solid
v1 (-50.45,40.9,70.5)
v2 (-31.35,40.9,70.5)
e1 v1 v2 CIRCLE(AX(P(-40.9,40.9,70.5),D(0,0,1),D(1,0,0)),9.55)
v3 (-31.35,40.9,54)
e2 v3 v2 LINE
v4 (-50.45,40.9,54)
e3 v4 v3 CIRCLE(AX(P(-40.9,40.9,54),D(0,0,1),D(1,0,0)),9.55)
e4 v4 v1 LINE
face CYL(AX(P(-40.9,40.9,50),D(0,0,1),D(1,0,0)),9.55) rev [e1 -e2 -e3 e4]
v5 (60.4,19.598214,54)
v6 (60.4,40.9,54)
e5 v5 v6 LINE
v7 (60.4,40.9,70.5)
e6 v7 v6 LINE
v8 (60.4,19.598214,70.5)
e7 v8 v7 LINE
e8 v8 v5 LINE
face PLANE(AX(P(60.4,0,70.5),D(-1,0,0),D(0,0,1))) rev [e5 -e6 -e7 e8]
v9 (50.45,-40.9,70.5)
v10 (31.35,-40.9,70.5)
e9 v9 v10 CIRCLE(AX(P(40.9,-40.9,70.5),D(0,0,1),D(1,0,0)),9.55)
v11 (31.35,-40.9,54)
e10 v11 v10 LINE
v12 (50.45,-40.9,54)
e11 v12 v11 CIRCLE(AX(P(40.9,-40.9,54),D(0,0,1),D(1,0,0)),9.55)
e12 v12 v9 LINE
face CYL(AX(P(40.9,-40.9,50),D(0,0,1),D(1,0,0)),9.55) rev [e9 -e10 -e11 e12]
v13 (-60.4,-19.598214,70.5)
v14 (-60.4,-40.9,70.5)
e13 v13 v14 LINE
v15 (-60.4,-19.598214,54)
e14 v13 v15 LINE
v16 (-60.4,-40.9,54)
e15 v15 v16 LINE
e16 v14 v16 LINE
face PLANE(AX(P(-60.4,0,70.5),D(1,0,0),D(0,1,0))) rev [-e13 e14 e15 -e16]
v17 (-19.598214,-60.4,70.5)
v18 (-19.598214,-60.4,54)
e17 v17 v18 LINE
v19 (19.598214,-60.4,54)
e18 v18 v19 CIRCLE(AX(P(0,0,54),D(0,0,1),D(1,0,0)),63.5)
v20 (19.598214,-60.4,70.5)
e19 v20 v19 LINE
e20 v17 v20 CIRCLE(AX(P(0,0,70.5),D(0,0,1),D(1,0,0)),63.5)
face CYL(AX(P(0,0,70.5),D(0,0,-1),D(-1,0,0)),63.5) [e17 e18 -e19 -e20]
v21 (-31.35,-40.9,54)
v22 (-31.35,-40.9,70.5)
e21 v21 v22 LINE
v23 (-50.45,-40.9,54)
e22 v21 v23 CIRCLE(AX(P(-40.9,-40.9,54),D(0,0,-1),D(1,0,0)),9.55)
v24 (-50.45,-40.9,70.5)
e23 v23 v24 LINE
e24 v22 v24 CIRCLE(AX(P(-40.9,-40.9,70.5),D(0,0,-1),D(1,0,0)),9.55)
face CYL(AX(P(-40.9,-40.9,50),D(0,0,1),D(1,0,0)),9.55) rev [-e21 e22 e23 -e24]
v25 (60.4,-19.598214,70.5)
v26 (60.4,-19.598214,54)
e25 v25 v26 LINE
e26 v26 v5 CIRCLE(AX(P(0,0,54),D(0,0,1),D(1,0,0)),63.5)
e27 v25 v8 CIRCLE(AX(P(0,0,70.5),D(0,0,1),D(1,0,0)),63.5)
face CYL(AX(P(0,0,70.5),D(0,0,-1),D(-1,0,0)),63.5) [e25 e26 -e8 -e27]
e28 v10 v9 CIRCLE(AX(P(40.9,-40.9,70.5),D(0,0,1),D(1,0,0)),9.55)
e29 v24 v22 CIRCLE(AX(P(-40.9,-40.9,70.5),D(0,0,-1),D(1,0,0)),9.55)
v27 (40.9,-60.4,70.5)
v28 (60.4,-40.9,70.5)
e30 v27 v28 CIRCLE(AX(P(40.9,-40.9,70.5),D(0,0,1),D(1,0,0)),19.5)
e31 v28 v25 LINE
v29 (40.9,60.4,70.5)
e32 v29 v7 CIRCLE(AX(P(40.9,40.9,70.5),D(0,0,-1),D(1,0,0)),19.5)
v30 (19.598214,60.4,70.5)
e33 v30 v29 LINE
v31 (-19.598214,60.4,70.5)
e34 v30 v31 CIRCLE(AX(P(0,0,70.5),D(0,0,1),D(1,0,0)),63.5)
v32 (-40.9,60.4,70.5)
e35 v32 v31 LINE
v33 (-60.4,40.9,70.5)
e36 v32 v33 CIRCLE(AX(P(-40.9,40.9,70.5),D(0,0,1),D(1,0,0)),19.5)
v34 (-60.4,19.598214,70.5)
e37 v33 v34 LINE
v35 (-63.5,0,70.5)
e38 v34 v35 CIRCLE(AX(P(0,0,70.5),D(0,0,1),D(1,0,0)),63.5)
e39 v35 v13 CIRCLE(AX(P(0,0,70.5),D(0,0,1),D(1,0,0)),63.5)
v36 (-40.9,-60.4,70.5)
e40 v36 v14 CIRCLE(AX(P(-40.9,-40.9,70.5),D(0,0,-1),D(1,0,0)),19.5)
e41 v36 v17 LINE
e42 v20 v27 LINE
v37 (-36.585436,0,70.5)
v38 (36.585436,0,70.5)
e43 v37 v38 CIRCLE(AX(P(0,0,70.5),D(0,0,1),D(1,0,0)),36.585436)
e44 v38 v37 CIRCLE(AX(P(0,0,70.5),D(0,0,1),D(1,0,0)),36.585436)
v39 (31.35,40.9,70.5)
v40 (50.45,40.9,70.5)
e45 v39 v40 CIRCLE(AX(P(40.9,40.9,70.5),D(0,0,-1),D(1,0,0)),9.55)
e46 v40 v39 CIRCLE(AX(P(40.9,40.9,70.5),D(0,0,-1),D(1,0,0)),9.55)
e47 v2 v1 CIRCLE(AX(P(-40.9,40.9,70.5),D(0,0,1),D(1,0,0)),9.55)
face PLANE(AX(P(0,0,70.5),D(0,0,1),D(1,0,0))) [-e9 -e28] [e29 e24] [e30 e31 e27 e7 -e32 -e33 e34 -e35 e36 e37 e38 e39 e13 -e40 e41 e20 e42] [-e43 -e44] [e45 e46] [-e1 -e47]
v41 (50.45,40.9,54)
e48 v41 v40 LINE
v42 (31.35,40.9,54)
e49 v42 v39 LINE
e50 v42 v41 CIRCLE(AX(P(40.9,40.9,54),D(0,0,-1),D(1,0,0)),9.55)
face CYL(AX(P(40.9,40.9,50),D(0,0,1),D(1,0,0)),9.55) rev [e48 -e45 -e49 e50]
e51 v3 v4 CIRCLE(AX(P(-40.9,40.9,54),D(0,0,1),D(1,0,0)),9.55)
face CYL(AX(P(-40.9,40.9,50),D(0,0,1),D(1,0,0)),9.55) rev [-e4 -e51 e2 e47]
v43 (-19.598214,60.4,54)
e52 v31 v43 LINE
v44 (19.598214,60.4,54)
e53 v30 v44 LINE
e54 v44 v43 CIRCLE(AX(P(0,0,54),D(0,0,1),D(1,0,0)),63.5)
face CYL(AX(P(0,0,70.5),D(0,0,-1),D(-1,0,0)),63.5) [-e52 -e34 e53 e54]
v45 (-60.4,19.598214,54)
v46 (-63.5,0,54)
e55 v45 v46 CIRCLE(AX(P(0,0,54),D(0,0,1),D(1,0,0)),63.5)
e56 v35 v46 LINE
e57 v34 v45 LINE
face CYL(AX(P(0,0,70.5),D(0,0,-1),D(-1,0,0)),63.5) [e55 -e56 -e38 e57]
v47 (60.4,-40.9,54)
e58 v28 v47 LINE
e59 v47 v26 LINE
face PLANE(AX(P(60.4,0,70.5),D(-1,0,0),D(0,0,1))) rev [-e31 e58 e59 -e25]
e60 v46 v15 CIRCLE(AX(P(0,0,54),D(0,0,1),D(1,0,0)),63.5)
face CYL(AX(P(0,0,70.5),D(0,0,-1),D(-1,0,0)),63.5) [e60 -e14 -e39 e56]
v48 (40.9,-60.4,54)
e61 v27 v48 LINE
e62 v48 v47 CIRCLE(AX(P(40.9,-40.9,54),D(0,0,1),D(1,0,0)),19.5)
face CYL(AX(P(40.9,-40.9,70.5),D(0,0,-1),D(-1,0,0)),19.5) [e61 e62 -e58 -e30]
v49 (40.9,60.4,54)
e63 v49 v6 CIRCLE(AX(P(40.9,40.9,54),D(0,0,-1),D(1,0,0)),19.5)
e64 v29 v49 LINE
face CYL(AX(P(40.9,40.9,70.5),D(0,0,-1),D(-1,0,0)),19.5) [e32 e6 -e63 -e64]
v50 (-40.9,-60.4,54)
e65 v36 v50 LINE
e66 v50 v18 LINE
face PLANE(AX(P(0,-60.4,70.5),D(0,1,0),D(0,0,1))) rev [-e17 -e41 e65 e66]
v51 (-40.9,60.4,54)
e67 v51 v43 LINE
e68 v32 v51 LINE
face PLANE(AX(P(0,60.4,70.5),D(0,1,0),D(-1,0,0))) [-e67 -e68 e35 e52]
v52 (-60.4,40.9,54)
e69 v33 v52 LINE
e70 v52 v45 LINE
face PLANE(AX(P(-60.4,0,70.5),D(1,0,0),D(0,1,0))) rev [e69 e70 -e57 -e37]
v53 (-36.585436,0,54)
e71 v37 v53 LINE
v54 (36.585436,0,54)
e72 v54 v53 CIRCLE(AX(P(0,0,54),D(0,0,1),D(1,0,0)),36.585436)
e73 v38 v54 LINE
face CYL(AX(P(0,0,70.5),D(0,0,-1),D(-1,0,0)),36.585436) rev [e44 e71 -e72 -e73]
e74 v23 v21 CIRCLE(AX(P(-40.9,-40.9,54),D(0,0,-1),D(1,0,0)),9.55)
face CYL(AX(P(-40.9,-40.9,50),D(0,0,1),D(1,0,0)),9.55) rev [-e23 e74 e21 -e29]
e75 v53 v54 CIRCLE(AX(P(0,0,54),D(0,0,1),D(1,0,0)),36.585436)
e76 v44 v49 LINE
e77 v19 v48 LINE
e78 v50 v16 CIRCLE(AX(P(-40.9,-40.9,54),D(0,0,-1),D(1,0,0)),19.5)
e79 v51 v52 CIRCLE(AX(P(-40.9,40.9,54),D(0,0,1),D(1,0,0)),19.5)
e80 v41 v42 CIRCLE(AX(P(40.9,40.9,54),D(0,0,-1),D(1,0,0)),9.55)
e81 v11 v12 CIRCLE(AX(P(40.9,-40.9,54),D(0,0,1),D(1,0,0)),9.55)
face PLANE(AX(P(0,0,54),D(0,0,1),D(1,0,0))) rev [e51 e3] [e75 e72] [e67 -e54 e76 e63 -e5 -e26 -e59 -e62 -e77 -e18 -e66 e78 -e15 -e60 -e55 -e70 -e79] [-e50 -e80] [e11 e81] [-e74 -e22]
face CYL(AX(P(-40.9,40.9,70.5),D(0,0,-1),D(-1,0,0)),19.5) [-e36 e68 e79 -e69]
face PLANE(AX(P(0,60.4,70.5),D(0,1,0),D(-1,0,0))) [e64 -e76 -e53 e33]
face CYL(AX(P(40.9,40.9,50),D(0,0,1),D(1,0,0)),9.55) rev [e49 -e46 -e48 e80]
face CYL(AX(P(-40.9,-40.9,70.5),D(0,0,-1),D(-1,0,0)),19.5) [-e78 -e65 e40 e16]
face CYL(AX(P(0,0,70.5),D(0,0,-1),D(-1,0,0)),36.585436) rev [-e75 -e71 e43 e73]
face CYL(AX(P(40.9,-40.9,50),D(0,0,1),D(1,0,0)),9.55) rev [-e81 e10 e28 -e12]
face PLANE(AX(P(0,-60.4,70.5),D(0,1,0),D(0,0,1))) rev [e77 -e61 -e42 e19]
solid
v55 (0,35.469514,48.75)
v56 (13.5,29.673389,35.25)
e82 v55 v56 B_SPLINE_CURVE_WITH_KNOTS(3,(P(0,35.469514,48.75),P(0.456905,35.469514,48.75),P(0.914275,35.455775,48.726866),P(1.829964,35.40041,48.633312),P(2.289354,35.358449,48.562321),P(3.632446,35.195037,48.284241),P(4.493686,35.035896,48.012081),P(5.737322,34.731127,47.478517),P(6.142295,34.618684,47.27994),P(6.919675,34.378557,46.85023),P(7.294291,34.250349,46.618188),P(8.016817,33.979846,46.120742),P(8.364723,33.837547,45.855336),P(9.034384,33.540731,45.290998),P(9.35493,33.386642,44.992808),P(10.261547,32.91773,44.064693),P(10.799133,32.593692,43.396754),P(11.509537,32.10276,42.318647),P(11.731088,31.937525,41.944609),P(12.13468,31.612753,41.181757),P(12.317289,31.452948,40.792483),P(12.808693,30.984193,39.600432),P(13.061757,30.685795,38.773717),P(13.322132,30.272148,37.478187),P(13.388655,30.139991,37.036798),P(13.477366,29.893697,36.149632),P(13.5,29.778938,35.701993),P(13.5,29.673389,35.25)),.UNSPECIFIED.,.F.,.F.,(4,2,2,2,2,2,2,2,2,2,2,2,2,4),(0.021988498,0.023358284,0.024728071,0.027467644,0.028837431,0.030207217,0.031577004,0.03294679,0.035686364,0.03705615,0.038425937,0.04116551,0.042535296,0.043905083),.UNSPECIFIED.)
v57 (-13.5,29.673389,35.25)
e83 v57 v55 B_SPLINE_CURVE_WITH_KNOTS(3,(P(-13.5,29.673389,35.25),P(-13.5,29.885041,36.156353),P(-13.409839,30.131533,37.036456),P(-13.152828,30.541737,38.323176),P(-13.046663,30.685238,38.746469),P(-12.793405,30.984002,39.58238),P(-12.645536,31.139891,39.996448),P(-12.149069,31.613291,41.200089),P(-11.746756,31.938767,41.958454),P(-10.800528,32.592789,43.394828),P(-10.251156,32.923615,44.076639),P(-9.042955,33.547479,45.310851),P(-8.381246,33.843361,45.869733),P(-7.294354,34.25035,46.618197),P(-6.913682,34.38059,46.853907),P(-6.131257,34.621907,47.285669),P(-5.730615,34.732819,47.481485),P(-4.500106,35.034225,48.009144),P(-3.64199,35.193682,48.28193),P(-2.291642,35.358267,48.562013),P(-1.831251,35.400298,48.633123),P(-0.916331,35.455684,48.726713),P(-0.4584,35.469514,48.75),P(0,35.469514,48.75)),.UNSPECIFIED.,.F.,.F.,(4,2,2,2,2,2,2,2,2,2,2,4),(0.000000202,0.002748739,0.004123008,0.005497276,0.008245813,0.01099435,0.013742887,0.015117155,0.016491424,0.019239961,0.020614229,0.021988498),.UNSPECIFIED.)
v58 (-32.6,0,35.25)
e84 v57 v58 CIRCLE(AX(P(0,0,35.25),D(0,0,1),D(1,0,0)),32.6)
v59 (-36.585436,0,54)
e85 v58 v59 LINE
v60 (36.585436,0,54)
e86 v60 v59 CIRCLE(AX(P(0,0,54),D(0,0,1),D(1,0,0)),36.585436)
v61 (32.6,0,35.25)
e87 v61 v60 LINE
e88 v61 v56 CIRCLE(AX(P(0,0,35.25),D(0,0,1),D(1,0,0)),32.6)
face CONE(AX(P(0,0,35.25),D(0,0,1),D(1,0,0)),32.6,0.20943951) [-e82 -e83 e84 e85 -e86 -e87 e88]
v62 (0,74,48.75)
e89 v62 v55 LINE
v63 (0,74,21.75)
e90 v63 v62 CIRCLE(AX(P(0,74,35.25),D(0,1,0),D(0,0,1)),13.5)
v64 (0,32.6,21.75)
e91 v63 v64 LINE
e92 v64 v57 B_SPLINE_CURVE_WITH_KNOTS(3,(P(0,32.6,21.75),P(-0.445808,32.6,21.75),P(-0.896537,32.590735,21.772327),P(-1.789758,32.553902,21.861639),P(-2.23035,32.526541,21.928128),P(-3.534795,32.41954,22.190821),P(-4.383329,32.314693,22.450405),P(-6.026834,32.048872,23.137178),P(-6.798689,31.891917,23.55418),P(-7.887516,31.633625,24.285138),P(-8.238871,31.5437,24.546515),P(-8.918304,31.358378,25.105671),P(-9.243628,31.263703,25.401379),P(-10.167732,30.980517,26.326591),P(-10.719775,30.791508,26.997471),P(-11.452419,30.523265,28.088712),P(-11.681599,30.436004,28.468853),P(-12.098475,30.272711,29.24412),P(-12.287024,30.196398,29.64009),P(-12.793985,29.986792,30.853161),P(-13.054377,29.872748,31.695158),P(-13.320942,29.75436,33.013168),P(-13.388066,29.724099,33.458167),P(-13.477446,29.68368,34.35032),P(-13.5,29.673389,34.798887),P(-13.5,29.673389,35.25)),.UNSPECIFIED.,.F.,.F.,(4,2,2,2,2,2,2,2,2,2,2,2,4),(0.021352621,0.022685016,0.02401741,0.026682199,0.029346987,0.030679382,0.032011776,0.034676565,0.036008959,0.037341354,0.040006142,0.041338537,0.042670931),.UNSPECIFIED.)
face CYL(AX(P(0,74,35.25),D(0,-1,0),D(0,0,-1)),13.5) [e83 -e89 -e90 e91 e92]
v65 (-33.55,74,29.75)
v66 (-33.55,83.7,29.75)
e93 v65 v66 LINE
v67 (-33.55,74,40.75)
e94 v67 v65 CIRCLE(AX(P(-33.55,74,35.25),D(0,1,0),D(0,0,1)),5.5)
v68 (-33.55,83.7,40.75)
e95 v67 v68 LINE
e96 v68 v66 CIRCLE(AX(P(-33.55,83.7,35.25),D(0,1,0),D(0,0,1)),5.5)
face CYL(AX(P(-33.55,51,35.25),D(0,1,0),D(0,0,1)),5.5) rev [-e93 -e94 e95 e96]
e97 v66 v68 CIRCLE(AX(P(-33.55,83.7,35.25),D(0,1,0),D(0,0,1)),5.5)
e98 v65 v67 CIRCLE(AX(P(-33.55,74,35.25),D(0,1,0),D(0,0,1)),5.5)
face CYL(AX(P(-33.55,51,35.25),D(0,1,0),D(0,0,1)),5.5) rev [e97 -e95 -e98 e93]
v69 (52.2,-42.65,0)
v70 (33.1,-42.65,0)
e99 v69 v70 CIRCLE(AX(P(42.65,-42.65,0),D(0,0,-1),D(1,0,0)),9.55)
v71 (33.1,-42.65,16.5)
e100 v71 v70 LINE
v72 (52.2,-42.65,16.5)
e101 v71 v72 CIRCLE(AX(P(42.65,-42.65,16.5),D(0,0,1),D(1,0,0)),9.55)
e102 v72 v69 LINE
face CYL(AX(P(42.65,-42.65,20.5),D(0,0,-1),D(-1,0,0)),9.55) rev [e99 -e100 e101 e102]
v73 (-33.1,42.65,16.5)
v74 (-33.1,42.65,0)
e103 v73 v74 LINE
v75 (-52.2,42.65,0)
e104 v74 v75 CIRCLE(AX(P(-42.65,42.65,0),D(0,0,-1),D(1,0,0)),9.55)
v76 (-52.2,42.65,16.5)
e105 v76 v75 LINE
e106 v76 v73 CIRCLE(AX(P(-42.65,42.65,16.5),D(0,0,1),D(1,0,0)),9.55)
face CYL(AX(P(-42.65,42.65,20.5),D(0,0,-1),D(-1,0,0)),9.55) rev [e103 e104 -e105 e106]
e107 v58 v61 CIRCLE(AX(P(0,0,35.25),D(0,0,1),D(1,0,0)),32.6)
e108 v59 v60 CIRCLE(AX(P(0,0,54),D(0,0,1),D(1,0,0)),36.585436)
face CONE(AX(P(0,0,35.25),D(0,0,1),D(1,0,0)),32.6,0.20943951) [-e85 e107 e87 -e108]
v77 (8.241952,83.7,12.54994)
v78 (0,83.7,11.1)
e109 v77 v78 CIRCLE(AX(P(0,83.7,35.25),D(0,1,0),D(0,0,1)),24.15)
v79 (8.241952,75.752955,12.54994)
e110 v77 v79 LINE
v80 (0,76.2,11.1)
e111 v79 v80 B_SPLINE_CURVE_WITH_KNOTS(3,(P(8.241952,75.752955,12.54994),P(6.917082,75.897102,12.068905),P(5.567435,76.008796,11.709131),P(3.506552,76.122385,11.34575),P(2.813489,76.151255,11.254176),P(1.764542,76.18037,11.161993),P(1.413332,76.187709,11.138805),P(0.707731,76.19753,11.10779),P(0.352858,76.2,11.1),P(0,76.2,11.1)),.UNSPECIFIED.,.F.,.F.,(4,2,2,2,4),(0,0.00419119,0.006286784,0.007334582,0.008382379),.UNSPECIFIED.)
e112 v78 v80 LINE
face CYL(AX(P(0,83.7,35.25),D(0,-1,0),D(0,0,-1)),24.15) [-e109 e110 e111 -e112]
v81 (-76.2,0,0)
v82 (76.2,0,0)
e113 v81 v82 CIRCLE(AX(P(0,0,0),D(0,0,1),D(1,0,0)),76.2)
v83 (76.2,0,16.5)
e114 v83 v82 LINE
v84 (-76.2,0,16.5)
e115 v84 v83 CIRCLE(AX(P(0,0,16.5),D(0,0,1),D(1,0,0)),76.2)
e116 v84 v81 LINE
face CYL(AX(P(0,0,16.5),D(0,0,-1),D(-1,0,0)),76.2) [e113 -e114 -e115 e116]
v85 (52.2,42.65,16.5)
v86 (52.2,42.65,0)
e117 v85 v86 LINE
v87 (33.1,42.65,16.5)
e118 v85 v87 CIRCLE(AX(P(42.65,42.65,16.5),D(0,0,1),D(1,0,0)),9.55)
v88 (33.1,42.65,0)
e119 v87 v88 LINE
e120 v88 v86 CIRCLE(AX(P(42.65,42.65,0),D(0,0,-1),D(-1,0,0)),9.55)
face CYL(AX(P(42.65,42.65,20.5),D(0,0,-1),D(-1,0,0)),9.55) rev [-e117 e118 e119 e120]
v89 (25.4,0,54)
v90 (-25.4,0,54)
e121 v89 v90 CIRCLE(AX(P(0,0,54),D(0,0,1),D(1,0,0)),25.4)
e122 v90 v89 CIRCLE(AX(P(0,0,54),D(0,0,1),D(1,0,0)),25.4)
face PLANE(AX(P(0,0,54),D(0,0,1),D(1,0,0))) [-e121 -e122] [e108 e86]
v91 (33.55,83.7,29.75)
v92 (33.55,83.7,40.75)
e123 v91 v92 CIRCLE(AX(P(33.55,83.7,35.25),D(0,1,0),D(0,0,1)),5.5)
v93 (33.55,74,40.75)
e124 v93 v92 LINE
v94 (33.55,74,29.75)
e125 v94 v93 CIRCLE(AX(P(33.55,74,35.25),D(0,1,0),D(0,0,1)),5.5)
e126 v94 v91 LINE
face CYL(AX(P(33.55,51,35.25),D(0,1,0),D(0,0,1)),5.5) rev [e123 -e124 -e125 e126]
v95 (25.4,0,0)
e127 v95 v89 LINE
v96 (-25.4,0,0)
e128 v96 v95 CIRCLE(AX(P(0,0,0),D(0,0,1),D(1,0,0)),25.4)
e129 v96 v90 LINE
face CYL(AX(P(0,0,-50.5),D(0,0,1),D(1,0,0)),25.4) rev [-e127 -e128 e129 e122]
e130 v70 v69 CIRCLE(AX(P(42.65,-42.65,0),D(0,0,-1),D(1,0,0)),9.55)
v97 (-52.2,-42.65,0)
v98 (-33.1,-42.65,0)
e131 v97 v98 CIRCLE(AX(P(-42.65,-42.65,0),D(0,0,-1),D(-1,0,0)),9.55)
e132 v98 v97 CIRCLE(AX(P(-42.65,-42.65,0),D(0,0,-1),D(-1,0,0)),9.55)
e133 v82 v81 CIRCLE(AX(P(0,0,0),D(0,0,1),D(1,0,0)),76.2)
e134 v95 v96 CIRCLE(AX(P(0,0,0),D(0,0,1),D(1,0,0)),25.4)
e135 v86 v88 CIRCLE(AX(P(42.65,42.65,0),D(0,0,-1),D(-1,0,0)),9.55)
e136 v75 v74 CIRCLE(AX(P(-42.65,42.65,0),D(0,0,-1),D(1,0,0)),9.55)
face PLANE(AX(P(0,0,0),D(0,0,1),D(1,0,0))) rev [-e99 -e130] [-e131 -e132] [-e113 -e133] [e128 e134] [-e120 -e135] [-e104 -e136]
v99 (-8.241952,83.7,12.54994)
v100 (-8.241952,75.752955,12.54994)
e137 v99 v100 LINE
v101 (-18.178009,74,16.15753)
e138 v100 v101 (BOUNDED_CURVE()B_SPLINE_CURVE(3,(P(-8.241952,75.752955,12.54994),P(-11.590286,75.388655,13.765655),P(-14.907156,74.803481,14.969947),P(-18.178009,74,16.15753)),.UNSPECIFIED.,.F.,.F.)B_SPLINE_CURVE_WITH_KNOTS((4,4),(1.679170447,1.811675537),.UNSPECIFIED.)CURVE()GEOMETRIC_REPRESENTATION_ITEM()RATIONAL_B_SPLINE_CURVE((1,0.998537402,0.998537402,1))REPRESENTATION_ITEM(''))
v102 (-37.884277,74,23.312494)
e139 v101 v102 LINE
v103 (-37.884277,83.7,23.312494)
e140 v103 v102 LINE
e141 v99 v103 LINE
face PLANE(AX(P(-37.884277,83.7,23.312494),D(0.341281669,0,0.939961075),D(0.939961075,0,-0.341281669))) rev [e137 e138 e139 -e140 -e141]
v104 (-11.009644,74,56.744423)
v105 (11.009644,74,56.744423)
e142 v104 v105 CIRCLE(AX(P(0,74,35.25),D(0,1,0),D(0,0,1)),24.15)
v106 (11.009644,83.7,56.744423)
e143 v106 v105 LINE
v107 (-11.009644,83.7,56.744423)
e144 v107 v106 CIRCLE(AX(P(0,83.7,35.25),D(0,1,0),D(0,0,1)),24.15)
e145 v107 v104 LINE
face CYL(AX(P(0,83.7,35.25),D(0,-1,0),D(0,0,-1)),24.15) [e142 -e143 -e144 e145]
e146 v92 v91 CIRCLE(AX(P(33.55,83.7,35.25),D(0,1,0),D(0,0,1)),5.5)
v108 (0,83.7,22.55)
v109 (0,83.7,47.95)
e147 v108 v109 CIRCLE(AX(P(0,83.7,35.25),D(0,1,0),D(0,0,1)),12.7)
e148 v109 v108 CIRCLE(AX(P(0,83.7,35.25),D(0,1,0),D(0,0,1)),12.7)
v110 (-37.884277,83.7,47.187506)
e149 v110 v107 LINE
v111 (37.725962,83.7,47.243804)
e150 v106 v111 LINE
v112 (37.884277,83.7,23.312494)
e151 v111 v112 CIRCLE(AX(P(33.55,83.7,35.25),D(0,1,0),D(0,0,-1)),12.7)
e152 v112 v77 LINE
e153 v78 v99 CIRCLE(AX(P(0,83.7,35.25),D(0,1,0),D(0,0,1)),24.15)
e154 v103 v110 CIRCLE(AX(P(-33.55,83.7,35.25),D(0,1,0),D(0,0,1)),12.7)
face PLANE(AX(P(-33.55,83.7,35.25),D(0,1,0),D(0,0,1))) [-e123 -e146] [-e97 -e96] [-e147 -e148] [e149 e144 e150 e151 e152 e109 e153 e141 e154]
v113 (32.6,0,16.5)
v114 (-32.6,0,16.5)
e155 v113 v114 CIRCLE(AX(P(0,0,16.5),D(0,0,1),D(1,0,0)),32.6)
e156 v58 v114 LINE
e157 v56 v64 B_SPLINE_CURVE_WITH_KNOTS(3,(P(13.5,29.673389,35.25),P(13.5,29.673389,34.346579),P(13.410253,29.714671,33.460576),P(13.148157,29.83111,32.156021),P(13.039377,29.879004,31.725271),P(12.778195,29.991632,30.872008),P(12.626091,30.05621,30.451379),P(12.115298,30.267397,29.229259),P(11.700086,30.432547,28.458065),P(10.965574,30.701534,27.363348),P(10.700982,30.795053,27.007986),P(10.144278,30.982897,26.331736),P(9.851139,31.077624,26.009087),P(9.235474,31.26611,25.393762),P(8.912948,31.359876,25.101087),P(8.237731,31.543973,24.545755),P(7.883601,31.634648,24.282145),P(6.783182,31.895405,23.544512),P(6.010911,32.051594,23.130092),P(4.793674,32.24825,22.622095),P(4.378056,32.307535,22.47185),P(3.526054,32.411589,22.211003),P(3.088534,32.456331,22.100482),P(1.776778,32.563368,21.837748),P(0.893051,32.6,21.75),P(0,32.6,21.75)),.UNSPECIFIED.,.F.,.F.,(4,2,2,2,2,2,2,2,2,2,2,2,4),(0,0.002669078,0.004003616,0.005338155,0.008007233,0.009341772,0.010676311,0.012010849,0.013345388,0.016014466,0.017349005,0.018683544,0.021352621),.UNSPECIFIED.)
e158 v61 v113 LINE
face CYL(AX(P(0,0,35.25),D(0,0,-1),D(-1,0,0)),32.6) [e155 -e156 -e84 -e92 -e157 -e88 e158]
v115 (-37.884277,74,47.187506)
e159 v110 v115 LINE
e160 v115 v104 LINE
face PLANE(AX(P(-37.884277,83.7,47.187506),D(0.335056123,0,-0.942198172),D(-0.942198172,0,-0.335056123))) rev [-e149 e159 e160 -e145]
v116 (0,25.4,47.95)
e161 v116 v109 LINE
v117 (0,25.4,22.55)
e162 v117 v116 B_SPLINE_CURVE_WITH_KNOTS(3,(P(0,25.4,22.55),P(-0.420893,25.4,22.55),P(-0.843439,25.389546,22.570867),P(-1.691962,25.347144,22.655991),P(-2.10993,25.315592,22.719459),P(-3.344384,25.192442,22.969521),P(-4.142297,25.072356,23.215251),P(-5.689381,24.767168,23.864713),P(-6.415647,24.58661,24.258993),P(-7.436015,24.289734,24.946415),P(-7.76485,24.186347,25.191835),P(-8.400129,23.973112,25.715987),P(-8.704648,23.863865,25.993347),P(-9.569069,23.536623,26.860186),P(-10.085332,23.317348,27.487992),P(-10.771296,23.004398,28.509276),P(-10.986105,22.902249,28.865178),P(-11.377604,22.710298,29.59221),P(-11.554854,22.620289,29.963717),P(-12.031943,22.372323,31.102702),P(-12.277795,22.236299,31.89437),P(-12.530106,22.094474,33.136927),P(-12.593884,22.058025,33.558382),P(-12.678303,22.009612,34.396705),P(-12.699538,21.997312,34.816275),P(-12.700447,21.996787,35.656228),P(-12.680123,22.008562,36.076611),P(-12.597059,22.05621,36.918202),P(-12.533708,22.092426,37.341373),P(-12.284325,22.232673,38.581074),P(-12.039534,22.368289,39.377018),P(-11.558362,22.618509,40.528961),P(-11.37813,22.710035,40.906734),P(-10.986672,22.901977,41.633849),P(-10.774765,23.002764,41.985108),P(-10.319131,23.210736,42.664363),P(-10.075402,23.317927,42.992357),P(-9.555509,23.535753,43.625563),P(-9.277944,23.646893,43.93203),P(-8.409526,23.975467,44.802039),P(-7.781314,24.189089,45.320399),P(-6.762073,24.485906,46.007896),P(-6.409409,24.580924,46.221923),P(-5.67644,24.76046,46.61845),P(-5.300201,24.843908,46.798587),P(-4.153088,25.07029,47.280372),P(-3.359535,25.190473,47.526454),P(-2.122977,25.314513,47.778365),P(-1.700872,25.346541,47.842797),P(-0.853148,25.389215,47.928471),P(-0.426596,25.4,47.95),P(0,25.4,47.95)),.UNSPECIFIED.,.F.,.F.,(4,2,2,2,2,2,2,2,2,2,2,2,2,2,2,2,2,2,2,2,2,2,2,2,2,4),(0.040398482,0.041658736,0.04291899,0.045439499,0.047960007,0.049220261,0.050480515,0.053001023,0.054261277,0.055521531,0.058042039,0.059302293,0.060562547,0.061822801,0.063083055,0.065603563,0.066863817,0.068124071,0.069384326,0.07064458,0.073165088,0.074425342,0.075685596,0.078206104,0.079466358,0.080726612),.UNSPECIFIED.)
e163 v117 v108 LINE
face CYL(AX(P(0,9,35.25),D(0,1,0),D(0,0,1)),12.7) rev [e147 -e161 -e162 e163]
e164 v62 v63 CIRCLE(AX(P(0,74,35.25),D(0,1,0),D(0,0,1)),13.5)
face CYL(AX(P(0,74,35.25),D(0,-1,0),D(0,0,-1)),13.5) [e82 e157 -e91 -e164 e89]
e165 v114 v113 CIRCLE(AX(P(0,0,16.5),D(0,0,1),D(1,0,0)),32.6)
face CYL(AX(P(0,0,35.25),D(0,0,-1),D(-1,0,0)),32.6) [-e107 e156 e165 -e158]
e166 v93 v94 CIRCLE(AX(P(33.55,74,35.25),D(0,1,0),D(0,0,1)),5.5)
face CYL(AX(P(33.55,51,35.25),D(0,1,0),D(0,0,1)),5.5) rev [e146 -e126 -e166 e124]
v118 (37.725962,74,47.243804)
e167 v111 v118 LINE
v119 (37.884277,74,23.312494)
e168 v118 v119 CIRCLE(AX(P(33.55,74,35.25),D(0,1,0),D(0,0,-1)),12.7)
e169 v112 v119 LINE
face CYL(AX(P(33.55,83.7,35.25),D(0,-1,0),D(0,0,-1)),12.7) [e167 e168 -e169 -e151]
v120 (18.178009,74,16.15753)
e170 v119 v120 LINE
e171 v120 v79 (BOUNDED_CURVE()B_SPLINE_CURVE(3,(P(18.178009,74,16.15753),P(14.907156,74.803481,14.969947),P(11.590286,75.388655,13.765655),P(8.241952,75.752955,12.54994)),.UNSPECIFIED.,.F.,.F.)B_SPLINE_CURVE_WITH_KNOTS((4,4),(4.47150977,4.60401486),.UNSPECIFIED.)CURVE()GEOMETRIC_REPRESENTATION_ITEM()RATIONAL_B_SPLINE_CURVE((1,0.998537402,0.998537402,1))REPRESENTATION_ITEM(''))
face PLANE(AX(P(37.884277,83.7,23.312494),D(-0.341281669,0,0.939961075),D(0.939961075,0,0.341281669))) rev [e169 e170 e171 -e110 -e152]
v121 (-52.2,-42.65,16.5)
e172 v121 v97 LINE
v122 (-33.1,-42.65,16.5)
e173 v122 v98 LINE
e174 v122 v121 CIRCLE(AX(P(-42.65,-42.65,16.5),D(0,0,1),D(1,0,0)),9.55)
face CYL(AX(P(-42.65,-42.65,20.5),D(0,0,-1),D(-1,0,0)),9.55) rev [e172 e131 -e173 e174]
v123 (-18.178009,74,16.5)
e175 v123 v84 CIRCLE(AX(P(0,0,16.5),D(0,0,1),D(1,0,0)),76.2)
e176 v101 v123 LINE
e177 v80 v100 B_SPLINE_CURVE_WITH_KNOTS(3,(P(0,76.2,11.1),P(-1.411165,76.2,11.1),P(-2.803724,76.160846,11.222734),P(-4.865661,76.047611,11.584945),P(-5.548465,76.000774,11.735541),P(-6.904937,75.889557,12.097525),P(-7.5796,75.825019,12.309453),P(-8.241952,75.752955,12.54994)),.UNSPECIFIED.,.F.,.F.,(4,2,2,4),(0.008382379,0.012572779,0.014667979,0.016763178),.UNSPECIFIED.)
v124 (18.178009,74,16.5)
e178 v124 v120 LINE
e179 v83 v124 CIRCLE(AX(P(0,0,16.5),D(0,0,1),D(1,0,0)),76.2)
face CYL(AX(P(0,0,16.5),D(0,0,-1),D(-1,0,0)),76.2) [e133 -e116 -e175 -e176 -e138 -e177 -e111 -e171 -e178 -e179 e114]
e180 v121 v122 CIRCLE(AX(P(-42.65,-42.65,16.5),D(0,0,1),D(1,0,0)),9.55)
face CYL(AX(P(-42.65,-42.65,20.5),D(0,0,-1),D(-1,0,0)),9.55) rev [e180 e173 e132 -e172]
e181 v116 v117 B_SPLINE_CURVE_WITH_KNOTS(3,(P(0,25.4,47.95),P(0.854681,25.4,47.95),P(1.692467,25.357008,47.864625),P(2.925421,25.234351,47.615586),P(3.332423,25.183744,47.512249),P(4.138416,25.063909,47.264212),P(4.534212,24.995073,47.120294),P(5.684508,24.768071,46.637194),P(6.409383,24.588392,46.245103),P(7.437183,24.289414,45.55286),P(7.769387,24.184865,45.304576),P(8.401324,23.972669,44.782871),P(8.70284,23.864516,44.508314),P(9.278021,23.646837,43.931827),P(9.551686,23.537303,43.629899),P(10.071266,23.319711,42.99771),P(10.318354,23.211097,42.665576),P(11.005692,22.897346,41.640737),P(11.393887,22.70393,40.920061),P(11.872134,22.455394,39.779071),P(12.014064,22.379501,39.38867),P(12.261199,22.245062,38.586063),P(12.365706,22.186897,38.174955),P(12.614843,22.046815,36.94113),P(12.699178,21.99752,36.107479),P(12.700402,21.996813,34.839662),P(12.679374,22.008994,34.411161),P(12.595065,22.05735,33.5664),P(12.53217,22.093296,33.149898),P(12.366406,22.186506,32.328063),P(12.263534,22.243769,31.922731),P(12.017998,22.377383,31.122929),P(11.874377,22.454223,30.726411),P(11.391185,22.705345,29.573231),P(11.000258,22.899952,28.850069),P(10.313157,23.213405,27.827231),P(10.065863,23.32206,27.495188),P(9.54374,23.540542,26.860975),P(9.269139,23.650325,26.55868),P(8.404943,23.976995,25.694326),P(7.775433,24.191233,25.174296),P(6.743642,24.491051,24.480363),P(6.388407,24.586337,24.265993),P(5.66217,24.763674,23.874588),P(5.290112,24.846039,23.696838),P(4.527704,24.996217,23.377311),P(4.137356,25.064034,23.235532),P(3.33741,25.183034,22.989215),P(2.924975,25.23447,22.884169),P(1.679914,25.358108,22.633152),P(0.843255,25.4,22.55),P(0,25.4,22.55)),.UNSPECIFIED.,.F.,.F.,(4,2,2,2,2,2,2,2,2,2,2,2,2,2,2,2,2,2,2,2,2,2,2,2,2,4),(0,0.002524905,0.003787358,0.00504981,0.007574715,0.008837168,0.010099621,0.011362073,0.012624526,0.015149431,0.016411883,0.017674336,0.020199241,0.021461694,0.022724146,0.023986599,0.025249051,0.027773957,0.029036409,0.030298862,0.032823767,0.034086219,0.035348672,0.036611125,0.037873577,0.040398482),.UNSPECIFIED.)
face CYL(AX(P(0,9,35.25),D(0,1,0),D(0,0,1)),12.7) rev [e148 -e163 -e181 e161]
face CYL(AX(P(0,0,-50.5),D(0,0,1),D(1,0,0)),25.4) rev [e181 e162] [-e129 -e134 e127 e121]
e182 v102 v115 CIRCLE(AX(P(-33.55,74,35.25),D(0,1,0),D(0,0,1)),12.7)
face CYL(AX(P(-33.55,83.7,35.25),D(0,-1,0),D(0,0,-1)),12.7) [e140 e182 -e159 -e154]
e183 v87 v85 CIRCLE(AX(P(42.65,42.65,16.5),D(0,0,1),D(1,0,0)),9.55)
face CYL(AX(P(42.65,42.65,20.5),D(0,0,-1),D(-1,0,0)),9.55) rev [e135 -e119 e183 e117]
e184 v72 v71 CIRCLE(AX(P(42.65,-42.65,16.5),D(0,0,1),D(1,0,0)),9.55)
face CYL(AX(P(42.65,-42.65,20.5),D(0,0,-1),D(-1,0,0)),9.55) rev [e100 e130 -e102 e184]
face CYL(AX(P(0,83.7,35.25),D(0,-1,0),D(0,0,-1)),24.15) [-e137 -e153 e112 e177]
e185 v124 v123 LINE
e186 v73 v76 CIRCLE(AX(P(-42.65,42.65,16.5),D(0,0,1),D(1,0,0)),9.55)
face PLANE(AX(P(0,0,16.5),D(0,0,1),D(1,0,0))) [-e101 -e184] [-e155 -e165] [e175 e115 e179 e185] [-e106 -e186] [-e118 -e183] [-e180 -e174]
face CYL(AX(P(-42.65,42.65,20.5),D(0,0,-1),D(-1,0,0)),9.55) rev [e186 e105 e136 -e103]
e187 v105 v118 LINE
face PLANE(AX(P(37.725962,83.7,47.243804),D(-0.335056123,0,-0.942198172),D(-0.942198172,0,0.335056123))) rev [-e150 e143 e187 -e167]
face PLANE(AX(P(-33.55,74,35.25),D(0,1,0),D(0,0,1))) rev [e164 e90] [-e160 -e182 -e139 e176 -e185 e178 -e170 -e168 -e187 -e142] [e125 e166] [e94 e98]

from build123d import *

# Parameters (mm, degrees)
ROUND_FLANGE_SKETCH_R                 = 76.2
ROUND_FLANGE_152_4_DEPTH              = 16.5
HUB_SKETCH_R                          = 32.6
HUB_65_2_DEPTH                        = 18.75
TAPERED_NECK_SKETCH_R                 = 32.6
TAPERED_NECK_12DEG_DRAFT_DEPTH        = 18.75
TAPERED_NECK_12DEG_DRAFT_DRAFT        = -12
SQUARE_FLANGE_SKETCH_R                = 36.585435531
SQUARE_FLANGE_127_DEPTH               = 16.5
SQUARE_FLANGE_HOLES_SKETCH_R          = 9.55
SQUARE_FLANGE_HOLES_DEPTH             = 20.5
ROUND_FLANGE_BOLT_HOLES_SKETCH_R      = 9.55
ROUND_FLANGE_BOLT_HOLES_4X_19_1_DEPTH = 20.5
SQUARE_FLANGE_BORE_SKETCH_R           = 25.4
SQUARE_FLANGE_BORE_DEPTH              = 121
SIDE_PORT_BOSS_SKETCH_R               = 13.5
SIDE_PORT_BOSS_DEPTH                  = 74
PORT_PAD_DEPTH                        = 9.7
ROUND_FLANGE_BORE_SKETCH_R            = 25.4
ROUND_FLANGE_BORE_DEPTH               = 352.7
PAD_BOLT_HOLES_SKETCH_R               = 5.5
PAD_BOLT_HOLES_2X_DEPTH               = 32.7
SIDE_PORT_BORE_SKETCH_R               = 12.7
SIDE_PORT_BORE_DEPTH                  = 74.7


with BuildPart() as part:
    # Round Flange Sketch → Round Flange Ø152.4 (new body)
    with BuildSketch(Plane.XY):
        Circle(ROUND_FLANGE_SKETCH_R)
    extrude(amount=ROUND_FLANGE_152_4_DEPTH)

    # Hub Sketch → Hub Ø65.2 (add)
    with BuildSketch(Plane.XY.offset(16.5)):
        Circle(HUB_SKETCH_R)
    extrude(amount=HUB_65_2_DEPTH)


with BuildPart() as tapered_neck_12deg_draft_tool:
    # Tapered Neck Sketch → Tapered Neck 12deg Draft (with draft: the straight prism first)
    with BuildSketch(Plane.XY.offset(35.25)):
        Circle(TAPERED_NECK_SKETCH_R)
    extrude(amount=TAPERED_NECK_12DEG_DRAFT_DEPTH)
    # Tapered Neck 12deg Draft: the draft: its side faces are tilted about the plane it starts from
    tapered_neck_12deg_draft_sides = [tapered_neck_12deg_draft_tool.faces().sort_by_distance(p)[0] for p in [
        (-32.6, 0, 44.625),
    ]]
    draft(tapered_neck_12deg_draft_sides, Plane.XY.offset(35.25), TAPERED_NECK_12DEG_DRAFT_DRAFT)


with BuildPart() as part_1:
    add(part.part)

    # Tapered Neck 12deg Draft: add tapered_neck_12deg_draft_tool
    add(tapered_neck_12deg_draft_tool.part)

    # Round Flange Bolt Holes Sketch → Round Flange Bolt Holes 4xØ19.1 (cut)
    with BuildSketch(Plane(origin=(0, 0, 0), x_dir=(-1, 0, 0), z_dir=(0, 0, -1))):
        with Locations((42.65, -42.65)):
            Circle(ROUND_FLANGE_BOLT_HOLES_SKETCH_R)
        with Locations(Location((42.65, 42.65, 0), (0, 0, 180))):
            Circle(ROUND_FLANGE_BOLT_HOLES_SKETCH_R)
        with Locations(Location((-42.65, -42.65, 0), (0, 0, 180))):
            Circle(ROUND_FLANGE_BOLT_HOLES_SKETCH_R)
        with Locations((-42.65, 42.65)):
            Circle(ROUND_FLANGE_BOLT_HOLES_SKETCH_R)
    extrude(amount=-ROUND_FLANGE_BOLT_HOLES_4X_19_1_DEPTH, mode=Mode.SUBTRACT)

    # Square Flange Bore Sketch → Square Flange Bore (cut)
    with BuildSketch(Plane.XY.offset(70.5)):
        Circle(SQUARE_FLANGE_BORE_SKETCH_R)
    extrude(amount=-SQUARE_FLANGE_BORE_DEPTH, mode=Mode.SUBTRACT)

    # Side Port Boss Sketch → Side Port Boss (add)
    with BuildSketch(Plane(origin=(0, 0, 0), x_dir=(1, 0, 0), z_dir=(0, 1, 0))):
        with Locations(Location((0, -35.25, 0), (0, 0, 90))):
            Circle(SIDE_PORT_BOSS_SKETCH_R)
    extrude(amount=SIDE_PORT_BOSS_DEPTH)

    # Port Pad Sketch → Port Pad (add)
    with BuildSketch(Plane(origin=(0, 74, 0), x_dir=(1, 0, 0), z_dir=(0, 1, 0))):
        with BuildLine():
            Line((-37.884277198, -23.312494349), (-8.24195231, -12.549940041))
            ThreePointArc((-8.24195231, -12.549940041), (0, -11.1), (8.24195231, -12.549940041))
            Line((8.24195231, -12.549940041), (37.884277198, -23.312494349))
            ThreePointArc((37.884277198, -23.312494349), (46.249722111, -35.334013693), (37.725962102, -47.243804256))
            Line((37.725962102, -47.243804256), (11.009644458, -56.744423205))
            ThreePointArc((11.009644458, -56.744423205), (0, -59.4), (-11.009644458, -56.744423205))
            Line((-11.009644458, -56.744423205), (-37.884277198, -47.187505651))
            ThreePointArc((-37.884277198, -47.187505651), (-46.25, -35.25), (-37.884277198, -23.312494349))
        make_face()
    extrude(amount=PORT_PAD_DEPTH)

    # Round Flange Bore Sketch → Round Flange Bore (cut)
    with BuildSketch(Plane.XY.offset(54)):
        Circle(ROUND_FLANGE_BORE_SKETCH_R)
    extrude(amount=-ROUND_FLANGE_BORE_DEPTH, mode=Mode.SUBTRACT)

    # Pad Bolt Holes Sketch → Pad Bolt Holes 2x (cut)
    with BuildSketch(Plane(origin=(0, 83.7, 0), x_dir=(1, 0, 0), z_dir=(0, 1, 0))):
        with Locations(Location((33.55, -35.25, 0), (0, 0, 270))):
            Circle(PAD_BOLT_HOLES_SKETCH_R)
        with Locations(Location((-33.55, -35.25, 0), (0, 0, 270))):
            Circle(PAD_BOLT_HOLES_SKETCH_R)
    extrude(amount=-PAD_BOLT_HOLES_2X_DEPTH, mode=Mode.SUBTRACT)

    # Side Port Bore Sketch → Side Port Bore (cut)
    with BuildSketch(Plane(origin=(0, 83.7, 0), x_dir=(1, 0, 0), z_dir=(0, 1, 0))):
        with Locations(Location((0, -35.25, 0), (0, 0, 270))):
            Circle(SIDE_PORT_BORE_SKETCH_R)
    extrude(amount=-SIDE_PORT_BORE_DEPTH, mode=Mode.SUBTRACT)


with BuildPart() as body_2:
    # Square Flange Sketch → Square Flange 127 (new body)
    with BuildSketch(Plane.XY.offset(54)):
        with BuildLine():
            Line((-40.9, -60.4), (-19.598214204, -60.4))
            ThreePointArc((-19.598214204, -60.4), (0, -63.5), (19.598214204, -60.4))
            Line((19.598214204, -60.4), (40.9, -60.4))
            ThreePointArc((40.9, -60.4), (54.688582233, -54.688582233), (60.4, -40.9))
            Line((60.4, -40.9), (60.4, -19.598214204))
            ThreePointArc((60.4, -19.598214204), (63.5, 0), (60.4, 19.598214204))
            Line((60.4, 19.598214204), (60.4, 40.9))
            ThreePointArc((60.4, 40.9), (54.688582233, 54.688582233), (40.9, 60.4))
            Line((40.9, 60.4), (19.598214204, 60.4))
            ThreePointArc((19.598214204, 60.4), (0, 63.5), (-19.598214204, 60.4))
            Line((-19.598214204, 60.4), (-40.9, 60.4))
            ThreePointArc((-40.9, 60.4), (-54.688582233, 54.688582233), (-60.4, 40.9))
            Line((-60.4, 40.9), (-60.4, 19.598214204))
            ThreePointArc((-60.4, 19.598214204), (-63.5, 0), (-60.4, -19.598214204))
            Line((-60.4, -19.598214204), (-60.4, -40.9))
            ThreePointArc((-60.4, -40.9), (-54.688582233, -54.688582233), (-40.9, -60.4))
        make_face()
        Circle(SQUARE_FLANGE_SKETCH_R, mode=Mode.SUBTRACT)
    extrude(amount=SQUARE_FLANGE_127_DEPTH)

    # Square Flange Holes Sketch → Square Flange Holes (cut)
    with BuildSketch(Plane.XY.offset(70.5)):
        with Locations((-40.9, 40.9)):
            Circle(SQUARE_FLANGE_HOLES_SKETCH_R)
        with Locations((40.9, 40.9)):
            Circle(SQUARE_FLANGE_HOLES_SKETCH_R)
        with Locations((40.9, -40.9)):
            Circle(SQUARE_FLANGE_HOLES_SKETCH_R)
        with Locations((-40.9, -40.9)):
            Circle(SQUARE_FLANGE_HOLES_SKETCH_R)
    extrude(amount=-SQUARE_FLANGE_HOLES_DEPTH, mode=Mode.SUBTRACT)


solid = Compound([part_1.part, body_2.part])
